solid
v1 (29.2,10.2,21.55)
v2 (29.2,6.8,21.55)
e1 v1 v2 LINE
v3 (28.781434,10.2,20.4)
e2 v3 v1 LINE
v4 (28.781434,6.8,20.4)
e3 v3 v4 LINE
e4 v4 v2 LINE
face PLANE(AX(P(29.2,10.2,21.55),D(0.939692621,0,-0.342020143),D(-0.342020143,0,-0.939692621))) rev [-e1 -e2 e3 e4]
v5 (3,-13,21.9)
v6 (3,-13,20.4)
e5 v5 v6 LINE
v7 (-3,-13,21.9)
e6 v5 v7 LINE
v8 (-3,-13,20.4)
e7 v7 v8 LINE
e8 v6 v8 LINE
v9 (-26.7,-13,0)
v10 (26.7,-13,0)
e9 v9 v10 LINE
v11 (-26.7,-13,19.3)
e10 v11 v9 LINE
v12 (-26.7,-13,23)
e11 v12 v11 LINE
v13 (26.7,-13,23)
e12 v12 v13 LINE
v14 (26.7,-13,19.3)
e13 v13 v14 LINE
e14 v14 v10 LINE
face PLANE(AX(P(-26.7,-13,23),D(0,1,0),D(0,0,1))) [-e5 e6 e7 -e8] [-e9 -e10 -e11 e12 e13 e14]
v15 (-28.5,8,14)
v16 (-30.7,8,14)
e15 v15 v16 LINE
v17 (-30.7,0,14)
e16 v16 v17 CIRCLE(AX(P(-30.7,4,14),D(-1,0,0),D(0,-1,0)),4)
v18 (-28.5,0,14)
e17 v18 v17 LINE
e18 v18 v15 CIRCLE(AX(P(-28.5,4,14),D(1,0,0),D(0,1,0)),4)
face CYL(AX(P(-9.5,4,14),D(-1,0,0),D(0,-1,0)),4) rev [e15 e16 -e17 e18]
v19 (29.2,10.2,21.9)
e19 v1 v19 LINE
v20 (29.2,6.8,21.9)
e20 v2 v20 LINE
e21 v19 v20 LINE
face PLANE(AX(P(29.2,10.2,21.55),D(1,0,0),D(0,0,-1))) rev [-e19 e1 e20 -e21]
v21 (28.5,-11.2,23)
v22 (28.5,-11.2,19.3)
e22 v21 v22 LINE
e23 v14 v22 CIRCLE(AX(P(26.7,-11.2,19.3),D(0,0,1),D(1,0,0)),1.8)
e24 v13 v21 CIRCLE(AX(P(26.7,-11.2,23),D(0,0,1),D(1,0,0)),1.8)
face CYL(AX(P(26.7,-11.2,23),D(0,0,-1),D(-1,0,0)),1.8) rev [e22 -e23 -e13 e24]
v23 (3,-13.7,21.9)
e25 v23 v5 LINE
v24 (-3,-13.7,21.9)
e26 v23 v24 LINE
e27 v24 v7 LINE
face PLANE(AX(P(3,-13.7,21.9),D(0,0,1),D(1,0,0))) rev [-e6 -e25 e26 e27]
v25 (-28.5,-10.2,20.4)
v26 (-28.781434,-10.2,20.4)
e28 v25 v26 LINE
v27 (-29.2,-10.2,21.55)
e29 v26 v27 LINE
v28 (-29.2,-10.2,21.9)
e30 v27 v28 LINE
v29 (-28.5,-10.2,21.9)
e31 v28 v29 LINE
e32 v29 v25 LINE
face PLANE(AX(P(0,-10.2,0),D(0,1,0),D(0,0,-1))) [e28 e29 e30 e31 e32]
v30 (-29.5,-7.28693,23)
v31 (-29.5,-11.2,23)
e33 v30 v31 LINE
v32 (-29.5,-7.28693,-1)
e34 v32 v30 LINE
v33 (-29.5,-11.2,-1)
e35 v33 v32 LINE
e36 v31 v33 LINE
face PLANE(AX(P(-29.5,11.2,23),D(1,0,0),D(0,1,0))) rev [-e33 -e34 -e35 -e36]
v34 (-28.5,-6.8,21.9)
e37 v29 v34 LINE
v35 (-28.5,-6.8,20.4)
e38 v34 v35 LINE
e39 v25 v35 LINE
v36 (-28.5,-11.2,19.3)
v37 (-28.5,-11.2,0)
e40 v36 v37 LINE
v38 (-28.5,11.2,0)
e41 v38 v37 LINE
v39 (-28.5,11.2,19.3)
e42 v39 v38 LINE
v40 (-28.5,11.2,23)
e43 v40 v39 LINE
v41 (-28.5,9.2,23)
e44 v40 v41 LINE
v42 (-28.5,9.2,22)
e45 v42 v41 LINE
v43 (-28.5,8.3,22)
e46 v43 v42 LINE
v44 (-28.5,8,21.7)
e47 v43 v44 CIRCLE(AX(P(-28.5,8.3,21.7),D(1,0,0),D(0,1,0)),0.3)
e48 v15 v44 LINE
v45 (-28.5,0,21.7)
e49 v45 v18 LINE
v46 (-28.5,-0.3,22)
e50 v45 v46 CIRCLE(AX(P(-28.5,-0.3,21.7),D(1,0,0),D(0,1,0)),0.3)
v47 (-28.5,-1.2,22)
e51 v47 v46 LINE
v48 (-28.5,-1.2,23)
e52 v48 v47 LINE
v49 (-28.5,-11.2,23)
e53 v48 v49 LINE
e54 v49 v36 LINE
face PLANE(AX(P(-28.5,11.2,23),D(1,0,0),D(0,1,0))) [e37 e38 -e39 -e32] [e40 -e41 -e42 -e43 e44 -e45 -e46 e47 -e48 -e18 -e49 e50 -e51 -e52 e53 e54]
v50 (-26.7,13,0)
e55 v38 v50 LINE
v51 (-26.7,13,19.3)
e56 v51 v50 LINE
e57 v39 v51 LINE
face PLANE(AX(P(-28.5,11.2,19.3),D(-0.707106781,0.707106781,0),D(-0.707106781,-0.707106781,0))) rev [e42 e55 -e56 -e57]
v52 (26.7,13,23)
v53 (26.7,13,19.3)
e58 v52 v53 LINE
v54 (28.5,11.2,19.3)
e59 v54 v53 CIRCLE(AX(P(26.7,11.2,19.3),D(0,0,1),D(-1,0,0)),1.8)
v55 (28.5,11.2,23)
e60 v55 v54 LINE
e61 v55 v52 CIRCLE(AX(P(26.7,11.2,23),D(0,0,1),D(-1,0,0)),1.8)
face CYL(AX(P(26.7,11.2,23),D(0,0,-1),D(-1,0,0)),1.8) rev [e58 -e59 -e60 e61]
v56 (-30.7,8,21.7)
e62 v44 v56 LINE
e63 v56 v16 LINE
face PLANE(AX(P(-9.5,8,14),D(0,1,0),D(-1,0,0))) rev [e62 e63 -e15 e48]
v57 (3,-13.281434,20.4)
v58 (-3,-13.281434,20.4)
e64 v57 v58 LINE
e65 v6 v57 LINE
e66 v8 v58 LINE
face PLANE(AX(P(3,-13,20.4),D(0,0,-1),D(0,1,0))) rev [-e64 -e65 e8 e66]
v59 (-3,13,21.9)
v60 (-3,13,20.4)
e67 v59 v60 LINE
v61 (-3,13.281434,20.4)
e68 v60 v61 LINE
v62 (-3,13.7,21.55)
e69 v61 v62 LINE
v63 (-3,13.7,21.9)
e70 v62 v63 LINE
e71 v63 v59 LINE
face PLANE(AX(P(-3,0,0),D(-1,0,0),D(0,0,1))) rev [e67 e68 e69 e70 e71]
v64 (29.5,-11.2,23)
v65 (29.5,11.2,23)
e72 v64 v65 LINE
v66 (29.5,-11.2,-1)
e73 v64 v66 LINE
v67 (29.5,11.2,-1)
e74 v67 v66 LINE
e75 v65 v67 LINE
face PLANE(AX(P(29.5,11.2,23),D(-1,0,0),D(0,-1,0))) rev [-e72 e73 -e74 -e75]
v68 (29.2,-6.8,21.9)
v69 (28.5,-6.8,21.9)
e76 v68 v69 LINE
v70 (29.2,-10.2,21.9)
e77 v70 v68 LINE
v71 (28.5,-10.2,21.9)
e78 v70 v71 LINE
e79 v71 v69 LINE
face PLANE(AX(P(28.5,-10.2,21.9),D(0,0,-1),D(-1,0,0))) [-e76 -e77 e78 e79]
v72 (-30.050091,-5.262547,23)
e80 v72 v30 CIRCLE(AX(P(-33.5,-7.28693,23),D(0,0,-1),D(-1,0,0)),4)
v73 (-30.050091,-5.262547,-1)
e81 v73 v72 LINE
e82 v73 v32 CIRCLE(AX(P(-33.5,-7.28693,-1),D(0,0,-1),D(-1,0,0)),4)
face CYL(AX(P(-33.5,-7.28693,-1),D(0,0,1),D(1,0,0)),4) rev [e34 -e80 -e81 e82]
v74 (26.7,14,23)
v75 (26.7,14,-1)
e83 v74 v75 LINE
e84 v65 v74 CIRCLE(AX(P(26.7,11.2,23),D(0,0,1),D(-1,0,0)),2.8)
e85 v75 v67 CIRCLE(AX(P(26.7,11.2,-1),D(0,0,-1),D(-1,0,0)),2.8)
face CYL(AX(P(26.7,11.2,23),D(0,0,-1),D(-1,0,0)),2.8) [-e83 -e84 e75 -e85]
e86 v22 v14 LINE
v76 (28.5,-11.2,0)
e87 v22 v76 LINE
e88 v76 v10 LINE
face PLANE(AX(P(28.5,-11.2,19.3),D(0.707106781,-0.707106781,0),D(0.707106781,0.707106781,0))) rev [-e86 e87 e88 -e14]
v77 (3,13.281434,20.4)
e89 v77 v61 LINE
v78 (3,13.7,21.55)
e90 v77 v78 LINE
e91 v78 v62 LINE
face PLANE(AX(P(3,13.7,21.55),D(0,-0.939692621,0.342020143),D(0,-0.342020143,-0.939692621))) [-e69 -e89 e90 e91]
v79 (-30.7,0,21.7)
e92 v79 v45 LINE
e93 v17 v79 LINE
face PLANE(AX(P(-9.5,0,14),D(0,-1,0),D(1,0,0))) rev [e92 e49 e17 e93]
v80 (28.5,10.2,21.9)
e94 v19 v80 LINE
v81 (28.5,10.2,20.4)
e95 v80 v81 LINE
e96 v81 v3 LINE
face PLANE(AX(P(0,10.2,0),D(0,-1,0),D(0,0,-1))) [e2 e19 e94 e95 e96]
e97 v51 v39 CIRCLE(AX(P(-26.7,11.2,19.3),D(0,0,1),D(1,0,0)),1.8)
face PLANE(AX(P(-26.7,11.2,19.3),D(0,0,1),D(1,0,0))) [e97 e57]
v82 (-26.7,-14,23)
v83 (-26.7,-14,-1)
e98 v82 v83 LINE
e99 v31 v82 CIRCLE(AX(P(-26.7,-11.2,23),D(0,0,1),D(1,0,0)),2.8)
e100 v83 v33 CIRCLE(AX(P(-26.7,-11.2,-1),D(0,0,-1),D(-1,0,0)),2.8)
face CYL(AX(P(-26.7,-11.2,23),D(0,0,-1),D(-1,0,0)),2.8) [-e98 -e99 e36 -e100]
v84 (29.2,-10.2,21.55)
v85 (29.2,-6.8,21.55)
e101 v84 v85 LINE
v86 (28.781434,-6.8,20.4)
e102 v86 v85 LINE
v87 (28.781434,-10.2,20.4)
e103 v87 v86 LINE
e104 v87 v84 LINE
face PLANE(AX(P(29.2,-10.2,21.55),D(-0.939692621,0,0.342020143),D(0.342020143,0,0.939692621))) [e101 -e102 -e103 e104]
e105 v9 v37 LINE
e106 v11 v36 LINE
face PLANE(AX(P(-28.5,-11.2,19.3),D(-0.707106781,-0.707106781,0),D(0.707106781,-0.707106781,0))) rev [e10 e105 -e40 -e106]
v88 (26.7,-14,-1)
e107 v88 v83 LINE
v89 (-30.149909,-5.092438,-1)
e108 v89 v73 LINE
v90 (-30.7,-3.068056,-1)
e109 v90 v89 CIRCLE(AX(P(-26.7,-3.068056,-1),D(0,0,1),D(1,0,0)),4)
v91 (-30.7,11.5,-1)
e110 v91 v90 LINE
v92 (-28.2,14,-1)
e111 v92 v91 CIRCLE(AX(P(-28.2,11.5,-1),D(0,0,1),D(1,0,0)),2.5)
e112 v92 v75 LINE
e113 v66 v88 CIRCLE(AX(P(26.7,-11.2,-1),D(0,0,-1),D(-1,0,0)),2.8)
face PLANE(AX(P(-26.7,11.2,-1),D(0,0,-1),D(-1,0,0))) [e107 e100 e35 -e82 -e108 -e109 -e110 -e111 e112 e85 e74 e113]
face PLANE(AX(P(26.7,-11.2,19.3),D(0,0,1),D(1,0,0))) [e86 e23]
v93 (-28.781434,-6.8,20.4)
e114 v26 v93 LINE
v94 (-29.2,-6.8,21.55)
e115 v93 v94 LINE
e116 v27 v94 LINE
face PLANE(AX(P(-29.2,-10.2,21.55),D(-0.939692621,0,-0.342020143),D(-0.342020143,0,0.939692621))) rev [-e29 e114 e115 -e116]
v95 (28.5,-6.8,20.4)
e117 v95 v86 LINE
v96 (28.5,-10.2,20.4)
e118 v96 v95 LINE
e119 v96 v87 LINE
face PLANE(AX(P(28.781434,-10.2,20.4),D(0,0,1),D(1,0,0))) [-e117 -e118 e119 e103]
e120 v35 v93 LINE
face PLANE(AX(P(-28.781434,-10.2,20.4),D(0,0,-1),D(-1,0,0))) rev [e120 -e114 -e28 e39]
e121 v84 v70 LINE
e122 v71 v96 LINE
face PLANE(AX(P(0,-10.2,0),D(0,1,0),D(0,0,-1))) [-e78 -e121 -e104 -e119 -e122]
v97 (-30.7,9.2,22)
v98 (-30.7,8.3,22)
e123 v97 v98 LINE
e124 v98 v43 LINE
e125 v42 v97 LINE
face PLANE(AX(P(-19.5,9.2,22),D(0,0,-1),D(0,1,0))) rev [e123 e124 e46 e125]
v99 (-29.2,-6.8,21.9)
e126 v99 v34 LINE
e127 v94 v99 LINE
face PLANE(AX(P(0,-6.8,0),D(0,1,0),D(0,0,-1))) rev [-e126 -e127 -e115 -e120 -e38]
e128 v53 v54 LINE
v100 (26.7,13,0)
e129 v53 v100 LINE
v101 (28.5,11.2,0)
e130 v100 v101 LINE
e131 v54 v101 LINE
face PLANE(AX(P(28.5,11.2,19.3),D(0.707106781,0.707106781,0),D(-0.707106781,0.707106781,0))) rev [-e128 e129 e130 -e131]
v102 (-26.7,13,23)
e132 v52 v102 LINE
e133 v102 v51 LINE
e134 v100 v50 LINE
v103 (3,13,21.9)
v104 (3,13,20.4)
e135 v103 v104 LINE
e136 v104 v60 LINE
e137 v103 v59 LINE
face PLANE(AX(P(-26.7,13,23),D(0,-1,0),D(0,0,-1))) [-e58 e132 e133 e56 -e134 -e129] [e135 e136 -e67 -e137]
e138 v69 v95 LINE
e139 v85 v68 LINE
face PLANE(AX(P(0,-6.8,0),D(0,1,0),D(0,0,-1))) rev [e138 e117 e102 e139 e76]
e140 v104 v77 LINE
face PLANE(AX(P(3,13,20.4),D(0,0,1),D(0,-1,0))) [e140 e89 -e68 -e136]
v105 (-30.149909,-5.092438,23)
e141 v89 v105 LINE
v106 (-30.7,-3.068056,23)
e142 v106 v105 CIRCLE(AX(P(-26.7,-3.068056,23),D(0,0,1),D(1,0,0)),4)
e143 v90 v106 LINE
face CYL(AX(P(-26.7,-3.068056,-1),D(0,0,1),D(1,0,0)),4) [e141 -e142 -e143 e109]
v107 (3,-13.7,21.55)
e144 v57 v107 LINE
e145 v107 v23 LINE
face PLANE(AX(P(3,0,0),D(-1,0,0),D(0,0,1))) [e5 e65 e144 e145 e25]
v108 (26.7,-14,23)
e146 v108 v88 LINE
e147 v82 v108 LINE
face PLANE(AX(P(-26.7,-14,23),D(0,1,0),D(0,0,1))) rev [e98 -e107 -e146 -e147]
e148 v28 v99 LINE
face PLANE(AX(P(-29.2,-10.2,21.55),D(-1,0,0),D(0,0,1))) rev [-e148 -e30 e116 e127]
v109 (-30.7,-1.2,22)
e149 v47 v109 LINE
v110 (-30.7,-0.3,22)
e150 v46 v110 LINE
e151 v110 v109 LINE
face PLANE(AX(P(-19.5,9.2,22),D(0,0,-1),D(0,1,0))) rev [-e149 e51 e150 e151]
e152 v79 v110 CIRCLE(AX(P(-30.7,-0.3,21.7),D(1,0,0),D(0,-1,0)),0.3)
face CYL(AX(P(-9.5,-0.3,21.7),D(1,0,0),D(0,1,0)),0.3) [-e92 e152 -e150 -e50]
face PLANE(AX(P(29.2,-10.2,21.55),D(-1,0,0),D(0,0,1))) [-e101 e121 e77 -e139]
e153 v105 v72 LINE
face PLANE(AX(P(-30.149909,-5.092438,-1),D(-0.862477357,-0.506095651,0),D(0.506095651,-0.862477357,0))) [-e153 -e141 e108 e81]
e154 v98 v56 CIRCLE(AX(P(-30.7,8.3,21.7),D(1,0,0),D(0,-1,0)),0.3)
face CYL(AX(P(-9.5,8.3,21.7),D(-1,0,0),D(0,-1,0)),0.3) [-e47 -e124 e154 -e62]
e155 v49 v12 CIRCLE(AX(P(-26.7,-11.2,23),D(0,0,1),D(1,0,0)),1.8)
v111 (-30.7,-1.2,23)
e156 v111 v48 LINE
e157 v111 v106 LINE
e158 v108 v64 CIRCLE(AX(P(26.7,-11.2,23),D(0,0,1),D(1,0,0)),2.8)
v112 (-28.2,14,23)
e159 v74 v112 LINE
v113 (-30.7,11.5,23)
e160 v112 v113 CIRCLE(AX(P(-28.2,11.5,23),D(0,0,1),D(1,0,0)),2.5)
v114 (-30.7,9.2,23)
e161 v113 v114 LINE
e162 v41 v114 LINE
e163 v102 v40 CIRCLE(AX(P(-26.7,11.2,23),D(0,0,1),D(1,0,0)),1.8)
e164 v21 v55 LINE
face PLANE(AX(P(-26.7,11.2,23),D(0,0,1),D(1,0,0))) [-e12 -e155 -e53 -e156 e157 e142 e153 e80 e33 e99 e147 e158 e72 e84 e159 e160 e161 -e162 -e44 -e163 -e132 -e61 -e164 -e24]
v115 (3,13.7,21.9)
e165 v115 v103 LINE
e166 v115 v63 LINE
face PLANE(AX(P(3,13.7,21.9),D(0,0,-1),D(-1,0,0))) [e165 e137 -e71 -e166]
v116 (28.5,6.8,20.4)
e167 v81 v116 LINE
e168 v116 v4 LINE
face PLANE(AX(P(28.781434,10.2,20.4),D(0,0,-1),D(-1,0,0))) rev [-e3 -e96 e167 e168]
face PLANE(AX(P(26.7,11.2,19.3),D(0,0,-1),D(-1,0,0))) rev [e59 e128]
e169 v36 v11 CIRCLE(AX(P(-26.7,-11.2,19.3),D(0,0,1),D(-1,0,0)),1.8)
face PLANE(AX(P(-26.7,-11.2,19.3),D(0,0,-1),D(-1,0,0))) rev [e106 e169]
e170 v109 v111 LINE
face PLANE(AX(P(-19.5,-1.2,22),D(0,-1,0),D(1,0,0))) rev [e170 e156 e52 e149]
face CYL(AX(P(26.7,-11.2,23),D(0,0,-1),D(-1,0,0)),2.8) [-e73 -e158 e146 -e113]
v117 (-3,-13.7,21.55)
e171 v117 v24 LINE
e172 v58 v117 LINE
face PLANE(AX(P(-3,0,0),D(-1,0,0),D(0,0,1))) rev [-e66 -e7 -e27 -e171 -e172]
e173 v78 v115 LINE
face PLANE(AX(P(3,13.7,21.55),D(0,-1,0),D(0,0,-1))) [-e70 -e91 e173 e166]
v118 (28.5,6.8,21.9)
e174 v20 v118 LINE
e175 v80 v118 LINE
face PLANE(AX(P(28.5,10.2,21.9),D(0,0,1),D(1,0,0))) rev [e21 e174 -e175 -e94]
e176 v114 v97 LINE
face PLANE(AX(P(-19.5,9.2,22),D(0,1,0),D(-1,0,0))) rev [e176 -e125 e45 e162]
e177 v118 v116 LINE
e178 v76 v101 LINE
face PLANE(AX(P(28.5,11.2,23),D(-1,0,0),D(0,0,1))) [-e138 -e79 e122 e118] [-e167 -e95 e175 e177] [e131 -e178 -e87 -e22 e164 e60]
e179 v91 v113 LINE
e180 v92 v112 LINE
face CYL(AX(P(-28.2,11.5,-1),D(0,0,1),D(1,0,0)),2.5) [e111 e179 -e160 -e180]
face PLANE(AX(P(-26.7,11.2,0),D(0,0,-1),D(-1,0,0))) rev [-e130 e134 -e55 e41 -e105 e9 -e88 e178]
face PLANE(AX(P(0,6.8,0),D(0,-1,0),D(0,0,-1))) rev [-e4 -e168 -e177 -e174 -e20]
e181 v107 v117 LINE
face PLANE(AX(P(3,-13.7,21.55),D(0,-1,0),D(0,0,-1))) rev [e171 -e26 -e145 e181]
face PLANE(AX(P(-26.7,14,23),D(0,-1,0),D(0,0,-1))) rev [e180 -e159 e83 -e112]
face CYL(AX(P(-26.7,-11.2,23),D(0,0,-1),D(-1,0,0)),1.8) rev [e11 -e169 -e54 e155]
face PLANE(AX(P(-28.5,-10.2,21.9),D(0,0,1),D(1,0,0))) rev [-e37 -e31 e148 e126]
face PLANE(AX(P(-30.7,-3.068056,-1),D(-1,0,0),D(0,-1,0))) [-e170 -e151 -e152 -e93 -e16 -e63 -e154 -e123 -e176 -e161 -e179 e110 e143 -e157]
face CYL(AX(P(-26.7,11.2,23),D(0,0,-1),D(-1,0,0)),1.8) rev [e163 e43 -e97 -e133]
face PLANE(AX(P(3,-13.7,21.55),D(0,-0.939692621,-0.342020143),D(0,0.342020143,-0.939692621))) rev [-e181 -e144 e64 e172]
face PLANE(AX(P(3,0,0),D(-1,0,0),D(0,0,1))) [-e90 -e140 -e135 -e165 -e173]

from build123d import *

# Parameters (mm, degrees)
EXTRUDE_1_DEPTH       = 23
EXTRUDE_START         = 1
EXTRUDE_2_DEPTH       = 1
CUT_EXTRUDE_1_DEPTH   = 20
SKETCH_5_W            = 3.764983414
SKETCH_5_H            = 10.4
CUT_EXTRUDE_3_DEPTH   = 10
CUT_EXTRUDE_START     = 6.8
CUT_EXTRUDE_4_DEPTH   = 3.4
MIRROR_START          = 6.8
MIRROR_2_COPY_1_DEPTH = 3.4
FILLET_2_R            = 0.3
EXTRUDE_3_DEPTH       = 19.3
EXTRUDE_START_2       = -24
EXTRUDE_4_DEPTH       = 24
CUT_EXTRUDE_START_2   = -10
CUT_EXTRUDE_5_DEPTH   = 10
EXTRUDE_START_3       = -2.2
EXTRUDE_5_DEPTH       = 2.2
CUT_EXTRUDE_6_DEPTH   = 5
CUT_EXTRUDE_7_DEPTH   = 3


with BuildPart() as part:
    # 草图1 → 凸台-拉伸1 (new body)
    with BuildSketch(Plane.XY):
        with BuildLine():
            Line((-26.7, 14), (26.7, 14))
            ThreePointArc((26.7, 14), (28.679898987, 13.179898987), (29.5, 11.2))
            Line((29.5, 11.2), (29.5, -11.2))
            ThreePointArc((29.5, -11.2), (28.679898987, -13.179898987), (26.7, -14))
            Line((26.7, -14), (-26.7, -14))
            ThreePointArc((-26.7, -14), (-28.679898987, -13.179898987), (-29.5, -11.2))
            Line((-29.5, -11.2), (-29.5, 11.2))
            ThreePointArc((-29.5, 11.2), (-28.679898987, 13.179898987), (-26.7, 14))
        make_face()
        with BuildLine():
            Line((-26.7, 13), (26.7, 13))
            ThreePointArc((26.7, 13), (27.972792206, 12.472792206), (28.5, 11.2))
            Line((28.5, 11.2), (28.5, -11.2))
            ThreePointArc((28.5, -11.2), (27.972792206, -12.472792206), (26.7, -13))
            Line((26.7, -13), (-26.7, -13))
            ThreePointArc((-26.7, -13), (-27.972792206, -12.472792206), (-28.5, -11.2))
            Line((-28.5, -11.2), (-28.5, 11.2))
            ThreePointArc((-28.5, 11.2), (-27.972792206, 12.472792206), (-26.7, 13))
        make_face(mode=Mode.SUBTRACT)
    extrude(amount=EXTRUDE_1_DEPTH)

    # 草图2 → 凸台-拉伸2 (add)
    with BuildSketch(Plane(origin=(0, 0, 0), x_dir=(-1, 0, 0), z_dir=(0, 0, -1)).offset(EXTRUDE_START)):
        with BuildLine():
            Line((26.7, 14), (-26.7, 14))
            ThreePointArc((-26.7, 14), (-28.679898987, 13.179898987), (-29.5, 11.2))
            Line((-29.5, 11.2), (-29.5, -11.2))
            ThreePointArc((-29.5, -11.2), (-28.679898987, -13.179898987), (-26.7, -14))
            Line((-26.7, -14), (26.7, -14))
            ThreePointArc((26.7, -14), (28.679898987, -13.179898987), (29.5, -11.2))
            Line((29.5, -11.2), (29.5, 11.2))
            ThreePointArc((29.5, 11.2), (28.679898987, 13.179898987), (26.7, 14))
        make_face()
    extrude(amount=-EXTRUDE_2_DEPTH)

    # 草图3 → 切除-拉伸1 (cut)
    with BuildSketch(Plane.ZY.offset(29.5)):
        with BuildLine():
            Line((14, 8), (25.240812318, 8))
            Line((25.240812318, 8), (25.240812318, 0))
            Line((25.240812318, 0), (14, 0))
            ThreePointArc((14, 0), (10, 4), (14, 8))
        make_face()
    extrude(amount=-CUT_EXTRUDE_1_DEPTH, mode=Mode.SUBTRACT)

    # 草图5 → 切除-拉伸3 (cut)
    with BuildSketch(Plane.ZY.offset(29.5)):
        with Locations((23.882491707, 4)):
            Rectangle(SKETCH_5_W, SKETCH_5_H)
    extrude(amount=-CUT_EXTRUDE_3_DEPTH, mode=Mode.SUBTRACT)

    # 草图6 → 切除-拉伸4 (cut)
    with BuildSketch(Plane(origin=(0, 0, 0), x_dir=(1, 0, 0), z_dir=(0, 1, 0)).offset(CUT_EXTRUDE_START)):
        Polygon((-28.5, -21.9), (-29.2, -21.9), (-29.2, -21.55), (-28.781434231, -20.4), (-28.5, -20.4), align=None)
    cut_extrude_4 = extrude(amount=CUT_EXTRUDE_4_DEPTH, mode=Mode.SUBTRACT)

    # 镜向1: 切除-拉伸4 across plane
    add(cut_extrude_4.mirror(Plane.ZX), mode=Mode.SUBTRACT)

    # 镜向2: 切除-拉伸4 across plane
    add(cut_extrude_4.mirror(Plane(origin=(0, 0, 0), x_dir=(0, 0, 1), z_dir=(1, 0, 0))), mode=Mode.SUBTRACT)

    # 镜向2 copy 1 sketch → 镜向2 copy 1 (cut)
    with BuildSketch(Plane(origin=(0, 0, 0), x_dir=(-1, 0, 0), z_dir=(0, -1, 0)).offset(MIRROR_START)):
        Polygon((-28.5, -21.9), (-29.2, -21.9), (-29.2, -21.55), (-28.781434231, -20.4), (-28.5, -20.4), align=None)
    extrude(amount=MIRROR_2_COPY_1_DEPTH, mode=Mode.SUBTRACT)

    # 圆角2
    fillet_2_edges = [part.edges().sort_by_distance(p)[0] for p in [
        (-29, 0, 22),
        (-29, 8, 22),
    ]]
    fillet(fillet_2_edges, radius=FILLET_2_R)

    # 草图9 → 凸台-拉伸3 (add)
    with BuildSketch(Plane.XY):
        with BuildLine():
            Line((-28.5, 11.2), (-26.7, 13))
            ThreePointArc((-26.7, 13), (-27.972792206, 12.472792206), (-28.5, 11.2))
        make_face()
        with BuildLine():
            Line((28.5, 11.2), (26.7, 13))
            ThreePointArc((26.7, 13), (27.972792206, 12.472792206), (28.5, 11.2))
        make_face()
        with BuildLine():
            Line((28.5, -11.2), (26.7, -13))
            ThreePointArc((26.7, -13), (27.972792206, -12.472792206), (28.5, -11.2))
        make_face()
        with BuildLine():
            Line((-28.5, -11.2), (-26.7, -13))
            ThreePointArc((-26.7, -13), (-27.972792206, -12.472792206), (-28.5, -11.2))
        make_face()
    extrude(amount=EXTRUDE_3_DEPTH)

    # 草图11 → 凸台-拉伸4 (add)
    with BuildSketch(Plane.XY.offset(23).offset(EXTRUDE_START_2)):
        with BuildLine():
            Line((-30.7, -3.068055681), (-30.7, 11.5))
            ThreePointArc((-30.7, 11.5), (-29.967766953, 13.267766953), (-28.2, 14))
            Line((-28.2, 14), (-26.7, 14))
            ThreePointArc((-26.7, 14), (-28.679898987, 13.179898987), (-29.5, 11.2))
            Line((-29.5, 11.2), (-29.5, -7.286930049))
            ThreePointArc((-29.5, -7.286930049), (-29.639971651, -6.238034848), (-30.050090571, -5.262547444))
            Line((-30.050090571, -5.262547444), (-30.149909429, -5.092438287))
            ThreePointArc((-30.149909429, -5.092438287), (-30.560028349, -4.116950882), (-30.7, -3.068055681))
        make_face()
    extrude(amount=EXTRUDE_4_DEPTH)

    # 草图12 → 切除-拉伸5 (cut)
    with BuildSketch(Plane(origin=(-29.5, 0, 0), x_dir=(0, 0, -1), z_dir=(1, 0, 0)).offset(CUT_EXTRUDE_START_2)):
        with BuildLine():
            Line((-23, 9.2), (-23, -1.2))
            Line((-23, -1.2), (-22, -1.2))
            Line((-22, -1.2), (-22, -0.3))
            ThreePointArc((-22, -0.3), (-21.912132034, -0.087867966), (-21.7, 0))
            Line((-21.7, 0), (-14, 0))
            ThreePointArc((-14, 0), (-10, 4), (-14, 8))
            Line((-14, 8), (-21.7, 8))
            ThreePointArc((-21.7, 8), (-21.912132034, 8.087867966), (-22, 8.3))
            Line((-22, 8.3), (-22, 9.2))
            Line((-22, 9.2), (-23, 9.2))
        make_face()
    extrude(amount=CUT_EXTRUDE_5_DEPTH, mode=Mode.SUBTRACT)

    # 草图13 → 凸台-拉伸5 (add)
    with BuildSketch(Plane.XZ.offset(-8).offset(EXTRUDE_START_3)):
        Polygon((-28.5, 20.4), (-28.5, 21.9), (-29.2, 21.9), (-29.2, 21.55), (-28.781434231, 20.4), align=None)
    extrude(amount=EXTRUDE_5_DEPTH)

    # 草图14 → 切除-拉伸6 (cut)
    with BuildSketch(Plane.ZY.offset(29.2)):
        with BuildLine():
            Line((21.7, 8), (22.114153774, 8))
            Line((22.114153774, 8), (22, 8.3))
            ThreePointArc((22, 8.3), (21.912132034, 8.087867966), (21.7, 8))
        make_face()
    extrude(amount=-CUT_EXTRUDE_6_DEPTH, mode=Mode.SUBTRACT)

    # 草图10 → 切除-拉伸7 (cut, symmetric)
    with BuildSketch(Plane.ZY):
        Polygon((21.9, -13.7), (21.9, -13), (20.4, -13), (20.4, -13.281434231), (21.55, -13.7), align=None)
    cut_extrude_7 = extrude(amount=CUT_EXTRUDE_7_DEPTH, both=True, mode=Mode.SUBTRACT)

    # 镜向3: 切除-拉伸7 across plane
    add(cut_extrude_7.mirror(Plane.ZX), mode=Mode.SUBTRACT)


solid = part.part
